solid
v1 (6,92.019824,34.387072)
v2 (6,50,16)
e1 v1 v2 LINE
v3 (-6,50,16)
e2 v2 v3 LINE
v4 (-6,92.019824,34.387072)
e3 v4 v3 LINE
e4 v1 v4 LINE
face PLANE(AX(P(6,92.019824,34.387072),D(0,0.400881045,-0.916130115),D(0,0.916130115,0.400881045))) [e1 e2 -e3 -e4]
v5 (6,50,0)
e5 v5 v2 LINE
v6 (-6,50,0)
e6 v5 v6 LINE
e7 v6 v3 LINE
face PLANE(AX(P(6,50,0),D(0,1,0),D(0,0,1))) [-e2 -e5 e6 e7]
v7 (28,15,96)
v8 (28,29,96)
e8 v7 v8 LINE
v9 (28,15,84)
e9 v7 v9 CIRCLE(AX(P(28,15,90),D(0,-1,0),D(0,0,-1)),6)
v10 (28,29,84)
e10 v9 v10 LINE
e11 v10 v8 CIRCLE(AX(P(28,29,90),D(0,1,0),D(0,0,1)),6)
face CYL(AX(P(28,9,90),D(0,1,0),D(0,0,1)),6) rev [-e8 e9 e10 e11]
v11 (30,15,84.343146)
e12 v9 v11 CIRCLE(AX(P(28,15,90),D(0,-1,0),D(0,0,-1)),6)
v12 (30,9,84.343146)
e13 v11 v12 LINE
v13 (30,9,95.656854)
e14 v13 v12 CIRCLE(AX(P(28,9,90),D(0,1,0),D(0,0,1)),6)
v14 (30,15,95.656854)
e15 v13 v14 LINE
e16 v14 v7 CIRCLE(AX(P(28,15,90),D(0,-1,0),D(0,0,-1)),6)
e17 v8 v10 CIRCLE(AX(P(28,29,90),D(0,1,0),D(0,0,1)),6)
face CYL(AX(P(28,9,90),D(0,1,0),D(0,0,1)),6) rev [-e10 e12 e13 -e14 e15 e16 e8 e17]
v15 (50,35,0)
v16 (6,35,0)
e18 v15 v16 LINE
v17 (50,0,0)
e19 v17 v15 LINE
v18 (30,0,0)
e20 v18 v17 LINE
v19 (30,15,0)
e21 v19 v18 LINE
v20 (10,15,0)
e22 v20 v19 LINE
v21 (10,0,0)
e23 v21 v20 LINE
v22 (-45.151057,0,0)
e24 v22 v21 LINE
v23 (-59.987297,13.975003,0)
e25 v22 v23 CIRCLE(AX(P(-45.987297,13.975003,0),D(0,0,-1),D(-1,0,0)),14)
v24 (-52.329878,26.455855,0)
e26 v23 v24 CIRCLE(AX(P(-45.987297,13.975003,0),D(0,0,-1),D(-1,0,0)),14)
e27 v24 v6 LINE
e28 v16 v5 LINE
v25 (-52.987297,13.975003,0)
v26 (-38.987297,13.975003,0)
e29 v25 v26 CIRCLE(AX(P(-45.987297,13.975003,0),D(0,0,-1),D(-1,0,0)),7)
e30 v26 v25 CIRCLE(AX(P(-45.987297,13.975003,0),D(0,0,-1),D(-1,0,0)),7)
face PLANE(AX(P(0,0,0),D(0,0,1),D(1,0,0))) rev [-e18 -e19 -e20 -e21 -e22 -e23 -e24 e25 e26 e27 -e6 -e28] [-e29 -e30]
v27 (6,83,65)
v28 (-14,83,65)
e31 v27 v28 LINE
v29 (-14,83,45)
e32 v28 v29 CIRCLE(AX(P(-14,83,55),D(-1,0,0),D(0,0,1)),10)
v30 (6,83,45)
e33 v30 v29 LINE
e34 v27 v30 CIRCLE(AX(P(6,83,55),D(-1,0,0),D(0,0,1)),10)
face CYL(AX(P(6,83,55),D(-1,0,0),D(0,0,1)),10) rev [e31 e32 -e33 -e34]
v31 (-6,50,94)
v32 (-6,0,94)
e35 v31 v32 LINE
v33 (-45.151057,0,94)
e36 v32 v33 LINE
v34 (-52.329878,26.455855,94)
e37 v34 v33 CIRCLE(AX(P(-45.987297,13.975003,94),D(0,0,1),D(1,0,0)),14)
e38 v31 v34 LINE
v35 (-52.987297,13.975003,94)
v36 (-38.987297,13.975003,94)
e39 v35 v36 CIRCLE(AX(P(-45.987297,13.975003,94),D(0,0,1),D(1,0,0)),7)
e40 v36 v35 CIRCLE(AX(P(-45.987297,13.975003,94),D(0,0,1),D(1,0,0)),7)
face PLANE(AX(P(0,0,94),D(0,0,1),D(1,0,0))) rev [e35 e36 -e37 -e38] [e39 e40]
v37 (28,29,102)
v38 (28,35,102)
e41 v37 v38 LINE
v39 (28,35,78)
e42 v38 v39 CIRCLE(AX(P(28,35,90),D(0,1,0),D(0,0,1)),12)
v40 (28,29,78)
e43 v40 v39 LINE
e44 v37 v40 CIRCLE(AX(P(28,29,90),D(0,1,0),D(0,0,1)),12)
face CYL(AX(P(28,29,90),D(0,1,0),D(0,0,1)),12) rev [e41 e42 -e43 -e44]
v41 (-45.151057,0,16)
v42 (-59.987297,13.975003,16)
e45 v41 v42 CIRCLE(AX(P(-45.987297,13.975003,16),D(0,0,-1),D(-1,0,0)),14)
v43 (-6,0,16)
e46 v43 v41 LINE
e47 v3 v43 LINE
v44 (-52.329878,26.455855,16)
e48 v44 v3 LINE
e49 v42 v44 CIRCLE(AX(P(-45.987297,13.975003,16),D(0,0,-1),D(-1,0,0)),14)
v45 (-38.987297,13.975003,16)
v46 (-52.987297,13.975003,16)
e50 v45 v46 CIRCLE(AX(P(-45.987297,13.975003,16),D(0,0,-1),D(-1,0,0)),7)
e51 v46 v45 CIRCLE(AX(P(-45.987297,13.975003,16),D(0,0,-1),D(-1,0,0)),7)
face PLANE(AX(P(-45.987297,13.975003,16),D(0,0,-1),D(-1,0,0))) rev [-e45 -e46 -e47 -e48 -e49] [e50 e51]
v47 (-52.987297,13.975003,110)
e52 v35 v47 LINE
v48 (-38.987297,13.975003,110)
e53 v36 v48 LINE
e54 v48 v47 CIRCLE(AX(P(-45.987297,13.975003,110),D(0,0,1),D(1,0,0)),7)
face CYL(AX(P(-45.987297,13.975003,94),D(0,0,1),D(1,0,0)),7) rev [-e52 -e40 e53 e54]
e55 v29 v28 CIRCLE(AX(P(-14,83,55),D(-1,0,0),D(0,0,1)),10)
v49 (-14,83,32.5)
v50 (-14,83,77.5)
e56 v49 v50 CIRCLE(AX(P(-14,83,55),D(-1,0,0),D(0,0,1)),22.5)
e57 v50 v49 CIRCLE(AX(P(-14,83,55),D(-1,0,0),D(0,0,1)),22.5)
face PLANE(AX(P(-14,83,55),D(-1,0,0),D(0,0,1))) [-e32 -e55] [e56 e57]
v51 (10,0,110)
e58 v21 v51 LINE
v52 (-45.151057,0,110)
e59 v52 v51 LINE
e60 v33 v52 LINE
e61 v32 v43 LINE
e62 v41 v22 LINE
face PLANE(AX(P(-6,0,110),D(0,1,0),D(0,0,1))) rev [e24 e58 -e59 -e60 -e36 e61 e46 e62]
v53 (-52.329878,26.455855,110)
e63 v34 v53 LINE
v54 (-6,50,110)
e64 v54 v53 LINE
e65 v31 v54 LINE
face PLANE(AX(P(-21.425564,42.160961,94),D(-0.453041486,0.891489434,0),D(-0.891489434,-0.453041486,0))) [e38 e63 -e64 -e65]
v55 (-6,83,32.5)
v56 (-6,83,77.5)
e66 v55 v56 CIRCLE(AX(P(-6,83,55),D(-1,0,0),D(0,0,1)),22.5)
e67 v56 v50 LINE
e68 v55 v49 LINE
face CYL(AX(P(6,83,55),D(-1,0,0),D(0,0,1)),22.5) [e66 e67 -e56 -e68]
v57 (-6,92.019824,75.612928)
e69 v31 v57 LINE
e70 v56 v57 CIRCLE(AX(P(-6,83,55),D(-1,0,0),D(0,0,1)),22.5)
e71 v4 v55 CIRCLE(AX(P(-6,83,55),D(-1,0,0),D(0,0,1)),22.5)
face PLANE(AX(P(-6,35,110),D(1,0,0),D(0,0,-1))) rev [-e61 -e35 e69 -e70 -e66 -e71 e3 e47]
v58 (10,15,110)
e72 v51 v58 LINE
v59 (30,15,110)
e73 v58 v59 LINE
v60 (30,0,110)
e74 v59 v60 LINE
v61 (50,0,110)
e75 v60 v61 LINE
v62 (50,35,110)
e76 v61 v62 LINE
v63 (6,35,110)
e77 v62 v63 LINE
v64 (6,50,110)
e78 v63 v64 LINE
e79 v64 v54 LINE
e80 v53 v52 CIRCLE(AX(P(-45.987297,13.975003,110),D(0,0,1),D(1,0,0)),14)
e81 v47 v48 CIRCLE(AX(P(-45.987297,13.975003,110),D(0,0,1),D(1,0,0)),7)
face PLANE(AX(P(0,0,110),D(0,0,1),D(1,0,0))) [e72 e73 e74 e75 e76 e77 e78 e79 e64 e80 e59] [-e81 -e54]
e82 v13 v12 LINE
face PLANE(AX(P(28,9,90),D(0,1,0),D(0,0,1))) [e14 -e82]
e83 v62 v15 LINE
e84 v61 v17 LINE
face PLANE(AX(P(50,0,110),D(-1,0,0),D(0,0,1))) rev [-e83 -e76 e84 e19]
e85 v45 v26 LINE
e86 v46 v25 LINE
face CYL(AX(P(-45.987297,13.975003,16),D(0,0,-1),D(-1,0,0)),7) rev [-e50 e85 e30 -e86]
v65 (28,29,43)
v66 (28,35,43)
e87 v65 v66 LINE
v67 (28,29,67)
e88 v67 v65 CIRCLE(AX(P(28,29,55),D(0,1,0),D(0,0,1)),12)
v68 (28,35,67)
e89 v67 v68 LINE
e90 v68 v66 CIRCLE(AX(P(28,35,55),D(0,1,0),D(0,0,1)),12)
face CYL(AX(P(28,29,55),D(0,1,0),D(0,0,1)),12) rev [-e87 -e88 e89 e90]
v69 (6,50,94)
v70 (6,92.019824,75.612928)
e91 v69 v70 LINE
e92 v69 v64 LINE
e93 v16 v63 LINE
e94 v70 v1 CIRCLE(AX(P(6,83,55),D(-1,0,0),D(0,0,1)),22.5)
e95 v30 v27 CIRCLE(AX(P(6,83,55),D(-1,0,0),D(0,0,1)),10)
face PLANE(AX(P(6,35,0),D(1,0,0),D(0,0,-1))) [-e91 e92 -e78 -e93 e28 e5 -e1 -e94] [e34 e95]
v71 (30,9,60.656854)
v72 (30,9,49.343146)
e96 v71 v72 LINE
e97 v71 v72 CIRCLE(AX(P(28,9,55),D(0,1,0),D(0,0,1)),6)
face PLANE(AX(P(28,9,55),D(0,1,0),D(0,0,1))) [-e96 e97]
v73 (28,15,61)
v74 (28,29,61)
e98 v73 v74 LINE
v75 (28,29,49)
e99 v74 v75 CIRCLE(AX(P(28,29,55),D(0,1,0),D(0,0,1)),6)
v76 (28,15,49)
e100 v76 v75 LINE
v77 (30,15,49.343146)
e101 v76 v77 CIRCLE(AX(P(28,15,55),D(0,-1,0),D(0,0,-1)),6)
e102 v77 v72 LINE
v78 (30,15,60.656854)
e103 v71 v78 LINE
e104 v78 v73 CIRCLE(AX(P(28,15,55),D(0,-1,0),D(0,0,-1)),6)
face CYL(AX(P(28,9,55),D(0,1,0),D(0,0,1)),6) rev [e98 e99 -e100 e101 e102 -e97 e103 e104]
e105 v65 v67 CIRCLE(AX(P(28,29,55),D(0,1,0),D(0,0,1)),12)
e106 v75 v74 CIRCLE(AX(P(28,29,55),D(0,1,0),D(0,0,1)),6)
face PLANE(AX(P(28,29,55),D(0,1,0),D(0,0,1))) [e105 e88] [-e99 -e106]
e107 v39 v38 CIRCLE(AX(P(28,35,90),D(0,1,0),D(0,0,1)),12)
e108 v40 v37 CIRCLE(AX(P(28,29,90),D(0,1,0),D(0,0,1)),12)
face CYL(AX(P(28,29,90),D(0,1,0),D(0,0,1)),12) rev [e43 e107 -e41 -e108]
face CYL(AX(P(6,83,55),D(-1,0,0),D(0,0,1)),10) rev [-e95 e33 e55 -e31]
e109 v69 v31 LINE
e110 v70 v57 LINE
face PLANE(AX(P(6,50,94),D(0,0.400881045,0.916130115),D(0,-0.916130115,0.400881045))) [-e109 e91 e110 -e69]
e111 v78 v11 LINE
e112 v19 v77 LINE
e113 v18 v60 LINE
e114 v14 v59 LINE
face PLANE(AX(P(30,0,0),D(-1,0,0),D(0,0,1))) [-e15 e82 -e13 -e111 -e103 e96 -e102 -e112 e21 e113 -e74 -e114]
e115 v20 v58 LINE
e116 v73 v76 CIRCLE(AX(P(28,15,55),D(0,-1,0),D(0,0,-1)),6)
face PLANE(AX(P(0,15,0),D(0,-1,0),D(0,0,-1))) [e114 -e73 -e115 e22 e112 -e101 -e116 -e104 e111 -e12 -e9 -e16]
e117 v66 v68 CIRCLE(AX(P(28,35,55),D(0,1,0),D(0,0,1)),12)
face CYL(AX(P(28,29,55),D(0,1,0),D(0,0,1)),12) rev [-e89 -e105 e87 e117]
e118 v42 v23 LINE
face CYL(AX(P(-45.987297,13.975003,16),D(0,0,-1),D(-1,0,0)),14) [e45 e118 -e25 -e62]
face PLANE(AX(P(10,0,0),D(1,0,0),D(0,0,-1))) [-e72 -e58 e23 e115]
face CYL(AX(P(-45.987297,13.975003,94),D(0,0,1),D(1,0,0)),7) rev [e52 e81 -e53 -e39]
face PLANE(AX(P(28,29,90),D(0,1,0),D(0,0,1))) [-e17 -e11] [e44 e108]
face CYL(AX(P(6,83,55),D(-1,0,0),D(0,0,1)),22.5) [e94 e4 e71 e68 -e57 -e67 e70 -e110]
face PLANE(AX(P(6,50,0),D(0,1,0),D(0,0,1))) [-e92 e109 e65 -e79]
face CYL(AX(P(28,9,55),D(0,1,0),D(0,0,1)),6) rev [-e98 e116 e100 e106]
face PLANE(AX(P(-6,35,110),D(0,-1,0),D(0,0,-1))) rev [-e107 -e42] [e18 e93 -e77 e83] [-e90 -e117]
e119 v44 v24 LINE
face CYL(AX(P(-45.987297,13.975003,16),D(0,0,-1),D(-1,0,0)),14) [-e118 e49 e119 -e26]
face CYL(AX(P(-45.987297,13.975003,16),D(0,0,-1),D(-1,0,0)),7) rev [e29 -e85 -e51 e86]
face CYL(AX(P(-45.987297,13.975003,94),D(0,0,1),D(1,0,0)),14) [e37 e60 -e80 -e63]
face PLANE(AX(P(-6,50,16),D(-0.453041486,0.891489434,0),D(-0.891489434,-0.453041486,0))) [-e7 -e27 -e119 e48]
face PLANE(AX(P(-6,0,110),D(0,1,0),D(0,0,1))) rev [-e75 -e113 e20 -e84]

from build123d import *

# Parameters (mm, degrees)
BASE_BLOCK_SKETCH_W         = 56
BASE_BLOCK_SKETCH_H         = 35
BASE_BLOCK_DEPTH            = 110
BOTTOM_SLOT_SKETCH_W        = 20
BOTTOM_SLOT_SKETCH_H        = 15
BOTTOM_SLOT_DEPTH           = 110
SIDE_STEP_SKETCH_W          = 12
SIDE_STEP_SKETCH_H          = 15
SIDE_STEP_DEPTH             = 110
SIDE_LUG_1_DEPTH            = 16
SIDE_HOLE_1_SKETCH_R        = 7
SIDE_HOLE_1_DEPTH           = 16
SIDE_START                  = -16
SIDE_LUG_2_DEPTH            = 16
SIDE_HOLE_2_SKETCH_R        = 7
SIDE_HOLE_2_DEPTH           = 16
UPRIGHT_EAR_DEPTH           = 12
PIVOT_START                 = 8
PIVOT_BOSS_45_SKETCH_R      = 22.5
PIVOT_BOSS_45_DEPTH         = 8
PIVOT_BORE_20_SKETCH_R      = 10
PIVOT_BORE_20_DEPTH         = 20
COUNTERBORES_2X_24_SKETCH_R = 12
COUNTERBORES_2X_24_DEPTH    = 6
HOLES_2X_12_SKETCH_R        = 6
HOLES_2X_12_DEPTH           = 20


with BuildPart() as part:
    # Base Block Sketch → Base Block (new body)
    with BuildSketch(Plane.XY):
        with Locations((22, 17.5)):
            Rectangle(BASE_BLOCK_SKETCH_W, BASE_BLOCK_SKETCH_H)
    extrude(amount=BASE_BLOCK_DEPTH)

    # Bottom Slot Sketch → Bottom Slot (cut)
    with BuildSketch(Plane.XY.offset(110)):
        with Locations((20, 7.5)):
            Rectangle(BOTTOM_SLOT_SKETCH_W, BOTTOM_SLOT_SKETCH_H)
    extrude(amount=-BOTTOM_SLOT_DEPTH, mode=Mode.SUBTRACT)

    # Side Step Sketch → Side Step (add)
    with BuildSketch(Plane.XY.offset(110)):
        with Locations((0, 42.5)):
            Rectangle(SIDE_STEP_SKETCH_W, SIDE_STEP_SKETCH_H)
    extrude(amount=-SIDE_STEP_DEPTH)

    # Side Lug 1 Sketch → Side Lug 1 (add)
    with BuildSketch(Plane.XY.offset(110)):
        with BuildLine():
            Line((-45.151057186, 0), (-6, 0))
            Line((-6, 0), (-6, 50))
            Line((-6, 50), (-52.329877609, 26.455854883))
            ThreePointArc((-52.329877609, 26.455854883), (-59.498699864, 10.308671221), (-45.151057186, 0))
        make_face()
    extrude(amount=-SIDE_LUG_1_DEPTH)

    # Side Hole 1 Sketch → Side Hole 1 (cut)
    with BuildSketch(Plane.XY.offset(110)):
        with Locations((-45.987296801, 13.975002802)):
            Circle(SIDE_HOLE_1_SKETCH_R)
    extrude(amount=-SIDE_HOLE_1_DEPTH, mode=Mode.SUBTRACT)

    # Side Lug 2 Sketch → Side Lug 2 (add)
    with BuildSketch(Plane(origin=(0, 0, 0), x_dir=(-1, 0, 0), z_dir=(0, 0, -1)).offset(SIDE_START)):
        with BuildLine():
            Line((6, 50), (6, 0))
            Line((6, 0), (45.151057186, 0))
            ThreePointArc((45.151057186, 0), (59.498699864, 10.308671221), (52.329877609, 26.455854883))
            Line((52.329877609, 26.455854883), (6, 50))
        make_face()
    extrude(amount=SIDE_LUG_2_DEPTH)

    # Side Hole 2 Sketch → Side Hole 2 (cut)
    with BuildSketch(Plane(origin=(0, 0, 0), x_dir=(-1, 0, 0), z_dir=(0, 0, -1)).offset(SIDE_START)):
        with Locations(Location((45.987296801, 13.975002802, 0), (0, 0, 180))):
            Circle(SIDE_HOLE_2_SKETCH_R)
    extrude(amount=SIDE_HOLE_2_DEPTH, mode=Mode.SUBTRACT)

    # Upright Ear Sketch → Upright Ear (add)
    with BuildSketch(Plane.ZY.offset(6)):
        with BuildLine():
            Line((34.387072411, 92.019823514), (16, 50))
            Line((16, 50), (94, 50))
            Line((94, 50), (75.612927589, 92.019823514))
            ThreePointArc((75.612927589, 92.019823514), (55, 105.5), (34.387072411, 92.019823514))
        make_face()
    extrude(amount=-UPRIGHT_EAR_DEPTH)

    # Pivot Boss Ø45 Sketch → Pivot Boss Ø45 (add)
    with BuildSketch(Plane.ZY.offset(6).offset(PIVOT_START)):
        with Locations((55, 83)):
            Circle(PIVOT_BOSS_45_SKETCH_R)
    extrude(amount=-PIVOT_BOSS_45_DEPTH)

    # Pivot Bore Ø20 Sketch → Pivot Bore Ø20 (cut)
    with BuildSketch(Plane.ZY.offset(14)):
        with Locations((55, 83)):
            Circle(PIVOT_BORE_20_SKETCH_R)
    extrude(amount=-PIVOT_BORE_20_DEPTH, mode=Mode.SUBTRACT)

    # Counterbores 2xØ24 Sketch → Counterbores 2xØ24 (cut)
    with BuildSketch(Plane(origin=(0, 35, 0), x_dir=(1, 0, 0), z_dir=(0, 1, 0))):
        with Locations(Location((28, -90, 0), (0, 0, 270))):
            Circle(COUNTERBORES_2X_24_SKETCH_R)
        with Locations(Location((28, -55, 0), (0, 0, 270))):
            Circle(COUNTERBORES_2X_24_SKETCH_R)
    extrude(amount=-COUNTERBORES_2X_24_DEPTH, mode=Mode.SUBTRACT)

    # Holes 2xØ12 Sketch → Holes 2xØ12 (cut)
    with BuildSketch(Plane(origin=(0, 29, 0), x_dir=(1, 0, 0), z_dir=(0, 1, 0))):
        with Locations(Location((28, -55, 0), (0, 0, 270))):
            Circle(HOLES_2X_12_SKETCH_R)
        with Locations(Location((28, -90, 0), (0, 0, 270))):
            Circle(HOLES_2X_12_SKETCH_R)
    extrude(amount=-HOLES_2X_12_DEPTH, mode=Mode.SUBTRACT)


solid = part.part
